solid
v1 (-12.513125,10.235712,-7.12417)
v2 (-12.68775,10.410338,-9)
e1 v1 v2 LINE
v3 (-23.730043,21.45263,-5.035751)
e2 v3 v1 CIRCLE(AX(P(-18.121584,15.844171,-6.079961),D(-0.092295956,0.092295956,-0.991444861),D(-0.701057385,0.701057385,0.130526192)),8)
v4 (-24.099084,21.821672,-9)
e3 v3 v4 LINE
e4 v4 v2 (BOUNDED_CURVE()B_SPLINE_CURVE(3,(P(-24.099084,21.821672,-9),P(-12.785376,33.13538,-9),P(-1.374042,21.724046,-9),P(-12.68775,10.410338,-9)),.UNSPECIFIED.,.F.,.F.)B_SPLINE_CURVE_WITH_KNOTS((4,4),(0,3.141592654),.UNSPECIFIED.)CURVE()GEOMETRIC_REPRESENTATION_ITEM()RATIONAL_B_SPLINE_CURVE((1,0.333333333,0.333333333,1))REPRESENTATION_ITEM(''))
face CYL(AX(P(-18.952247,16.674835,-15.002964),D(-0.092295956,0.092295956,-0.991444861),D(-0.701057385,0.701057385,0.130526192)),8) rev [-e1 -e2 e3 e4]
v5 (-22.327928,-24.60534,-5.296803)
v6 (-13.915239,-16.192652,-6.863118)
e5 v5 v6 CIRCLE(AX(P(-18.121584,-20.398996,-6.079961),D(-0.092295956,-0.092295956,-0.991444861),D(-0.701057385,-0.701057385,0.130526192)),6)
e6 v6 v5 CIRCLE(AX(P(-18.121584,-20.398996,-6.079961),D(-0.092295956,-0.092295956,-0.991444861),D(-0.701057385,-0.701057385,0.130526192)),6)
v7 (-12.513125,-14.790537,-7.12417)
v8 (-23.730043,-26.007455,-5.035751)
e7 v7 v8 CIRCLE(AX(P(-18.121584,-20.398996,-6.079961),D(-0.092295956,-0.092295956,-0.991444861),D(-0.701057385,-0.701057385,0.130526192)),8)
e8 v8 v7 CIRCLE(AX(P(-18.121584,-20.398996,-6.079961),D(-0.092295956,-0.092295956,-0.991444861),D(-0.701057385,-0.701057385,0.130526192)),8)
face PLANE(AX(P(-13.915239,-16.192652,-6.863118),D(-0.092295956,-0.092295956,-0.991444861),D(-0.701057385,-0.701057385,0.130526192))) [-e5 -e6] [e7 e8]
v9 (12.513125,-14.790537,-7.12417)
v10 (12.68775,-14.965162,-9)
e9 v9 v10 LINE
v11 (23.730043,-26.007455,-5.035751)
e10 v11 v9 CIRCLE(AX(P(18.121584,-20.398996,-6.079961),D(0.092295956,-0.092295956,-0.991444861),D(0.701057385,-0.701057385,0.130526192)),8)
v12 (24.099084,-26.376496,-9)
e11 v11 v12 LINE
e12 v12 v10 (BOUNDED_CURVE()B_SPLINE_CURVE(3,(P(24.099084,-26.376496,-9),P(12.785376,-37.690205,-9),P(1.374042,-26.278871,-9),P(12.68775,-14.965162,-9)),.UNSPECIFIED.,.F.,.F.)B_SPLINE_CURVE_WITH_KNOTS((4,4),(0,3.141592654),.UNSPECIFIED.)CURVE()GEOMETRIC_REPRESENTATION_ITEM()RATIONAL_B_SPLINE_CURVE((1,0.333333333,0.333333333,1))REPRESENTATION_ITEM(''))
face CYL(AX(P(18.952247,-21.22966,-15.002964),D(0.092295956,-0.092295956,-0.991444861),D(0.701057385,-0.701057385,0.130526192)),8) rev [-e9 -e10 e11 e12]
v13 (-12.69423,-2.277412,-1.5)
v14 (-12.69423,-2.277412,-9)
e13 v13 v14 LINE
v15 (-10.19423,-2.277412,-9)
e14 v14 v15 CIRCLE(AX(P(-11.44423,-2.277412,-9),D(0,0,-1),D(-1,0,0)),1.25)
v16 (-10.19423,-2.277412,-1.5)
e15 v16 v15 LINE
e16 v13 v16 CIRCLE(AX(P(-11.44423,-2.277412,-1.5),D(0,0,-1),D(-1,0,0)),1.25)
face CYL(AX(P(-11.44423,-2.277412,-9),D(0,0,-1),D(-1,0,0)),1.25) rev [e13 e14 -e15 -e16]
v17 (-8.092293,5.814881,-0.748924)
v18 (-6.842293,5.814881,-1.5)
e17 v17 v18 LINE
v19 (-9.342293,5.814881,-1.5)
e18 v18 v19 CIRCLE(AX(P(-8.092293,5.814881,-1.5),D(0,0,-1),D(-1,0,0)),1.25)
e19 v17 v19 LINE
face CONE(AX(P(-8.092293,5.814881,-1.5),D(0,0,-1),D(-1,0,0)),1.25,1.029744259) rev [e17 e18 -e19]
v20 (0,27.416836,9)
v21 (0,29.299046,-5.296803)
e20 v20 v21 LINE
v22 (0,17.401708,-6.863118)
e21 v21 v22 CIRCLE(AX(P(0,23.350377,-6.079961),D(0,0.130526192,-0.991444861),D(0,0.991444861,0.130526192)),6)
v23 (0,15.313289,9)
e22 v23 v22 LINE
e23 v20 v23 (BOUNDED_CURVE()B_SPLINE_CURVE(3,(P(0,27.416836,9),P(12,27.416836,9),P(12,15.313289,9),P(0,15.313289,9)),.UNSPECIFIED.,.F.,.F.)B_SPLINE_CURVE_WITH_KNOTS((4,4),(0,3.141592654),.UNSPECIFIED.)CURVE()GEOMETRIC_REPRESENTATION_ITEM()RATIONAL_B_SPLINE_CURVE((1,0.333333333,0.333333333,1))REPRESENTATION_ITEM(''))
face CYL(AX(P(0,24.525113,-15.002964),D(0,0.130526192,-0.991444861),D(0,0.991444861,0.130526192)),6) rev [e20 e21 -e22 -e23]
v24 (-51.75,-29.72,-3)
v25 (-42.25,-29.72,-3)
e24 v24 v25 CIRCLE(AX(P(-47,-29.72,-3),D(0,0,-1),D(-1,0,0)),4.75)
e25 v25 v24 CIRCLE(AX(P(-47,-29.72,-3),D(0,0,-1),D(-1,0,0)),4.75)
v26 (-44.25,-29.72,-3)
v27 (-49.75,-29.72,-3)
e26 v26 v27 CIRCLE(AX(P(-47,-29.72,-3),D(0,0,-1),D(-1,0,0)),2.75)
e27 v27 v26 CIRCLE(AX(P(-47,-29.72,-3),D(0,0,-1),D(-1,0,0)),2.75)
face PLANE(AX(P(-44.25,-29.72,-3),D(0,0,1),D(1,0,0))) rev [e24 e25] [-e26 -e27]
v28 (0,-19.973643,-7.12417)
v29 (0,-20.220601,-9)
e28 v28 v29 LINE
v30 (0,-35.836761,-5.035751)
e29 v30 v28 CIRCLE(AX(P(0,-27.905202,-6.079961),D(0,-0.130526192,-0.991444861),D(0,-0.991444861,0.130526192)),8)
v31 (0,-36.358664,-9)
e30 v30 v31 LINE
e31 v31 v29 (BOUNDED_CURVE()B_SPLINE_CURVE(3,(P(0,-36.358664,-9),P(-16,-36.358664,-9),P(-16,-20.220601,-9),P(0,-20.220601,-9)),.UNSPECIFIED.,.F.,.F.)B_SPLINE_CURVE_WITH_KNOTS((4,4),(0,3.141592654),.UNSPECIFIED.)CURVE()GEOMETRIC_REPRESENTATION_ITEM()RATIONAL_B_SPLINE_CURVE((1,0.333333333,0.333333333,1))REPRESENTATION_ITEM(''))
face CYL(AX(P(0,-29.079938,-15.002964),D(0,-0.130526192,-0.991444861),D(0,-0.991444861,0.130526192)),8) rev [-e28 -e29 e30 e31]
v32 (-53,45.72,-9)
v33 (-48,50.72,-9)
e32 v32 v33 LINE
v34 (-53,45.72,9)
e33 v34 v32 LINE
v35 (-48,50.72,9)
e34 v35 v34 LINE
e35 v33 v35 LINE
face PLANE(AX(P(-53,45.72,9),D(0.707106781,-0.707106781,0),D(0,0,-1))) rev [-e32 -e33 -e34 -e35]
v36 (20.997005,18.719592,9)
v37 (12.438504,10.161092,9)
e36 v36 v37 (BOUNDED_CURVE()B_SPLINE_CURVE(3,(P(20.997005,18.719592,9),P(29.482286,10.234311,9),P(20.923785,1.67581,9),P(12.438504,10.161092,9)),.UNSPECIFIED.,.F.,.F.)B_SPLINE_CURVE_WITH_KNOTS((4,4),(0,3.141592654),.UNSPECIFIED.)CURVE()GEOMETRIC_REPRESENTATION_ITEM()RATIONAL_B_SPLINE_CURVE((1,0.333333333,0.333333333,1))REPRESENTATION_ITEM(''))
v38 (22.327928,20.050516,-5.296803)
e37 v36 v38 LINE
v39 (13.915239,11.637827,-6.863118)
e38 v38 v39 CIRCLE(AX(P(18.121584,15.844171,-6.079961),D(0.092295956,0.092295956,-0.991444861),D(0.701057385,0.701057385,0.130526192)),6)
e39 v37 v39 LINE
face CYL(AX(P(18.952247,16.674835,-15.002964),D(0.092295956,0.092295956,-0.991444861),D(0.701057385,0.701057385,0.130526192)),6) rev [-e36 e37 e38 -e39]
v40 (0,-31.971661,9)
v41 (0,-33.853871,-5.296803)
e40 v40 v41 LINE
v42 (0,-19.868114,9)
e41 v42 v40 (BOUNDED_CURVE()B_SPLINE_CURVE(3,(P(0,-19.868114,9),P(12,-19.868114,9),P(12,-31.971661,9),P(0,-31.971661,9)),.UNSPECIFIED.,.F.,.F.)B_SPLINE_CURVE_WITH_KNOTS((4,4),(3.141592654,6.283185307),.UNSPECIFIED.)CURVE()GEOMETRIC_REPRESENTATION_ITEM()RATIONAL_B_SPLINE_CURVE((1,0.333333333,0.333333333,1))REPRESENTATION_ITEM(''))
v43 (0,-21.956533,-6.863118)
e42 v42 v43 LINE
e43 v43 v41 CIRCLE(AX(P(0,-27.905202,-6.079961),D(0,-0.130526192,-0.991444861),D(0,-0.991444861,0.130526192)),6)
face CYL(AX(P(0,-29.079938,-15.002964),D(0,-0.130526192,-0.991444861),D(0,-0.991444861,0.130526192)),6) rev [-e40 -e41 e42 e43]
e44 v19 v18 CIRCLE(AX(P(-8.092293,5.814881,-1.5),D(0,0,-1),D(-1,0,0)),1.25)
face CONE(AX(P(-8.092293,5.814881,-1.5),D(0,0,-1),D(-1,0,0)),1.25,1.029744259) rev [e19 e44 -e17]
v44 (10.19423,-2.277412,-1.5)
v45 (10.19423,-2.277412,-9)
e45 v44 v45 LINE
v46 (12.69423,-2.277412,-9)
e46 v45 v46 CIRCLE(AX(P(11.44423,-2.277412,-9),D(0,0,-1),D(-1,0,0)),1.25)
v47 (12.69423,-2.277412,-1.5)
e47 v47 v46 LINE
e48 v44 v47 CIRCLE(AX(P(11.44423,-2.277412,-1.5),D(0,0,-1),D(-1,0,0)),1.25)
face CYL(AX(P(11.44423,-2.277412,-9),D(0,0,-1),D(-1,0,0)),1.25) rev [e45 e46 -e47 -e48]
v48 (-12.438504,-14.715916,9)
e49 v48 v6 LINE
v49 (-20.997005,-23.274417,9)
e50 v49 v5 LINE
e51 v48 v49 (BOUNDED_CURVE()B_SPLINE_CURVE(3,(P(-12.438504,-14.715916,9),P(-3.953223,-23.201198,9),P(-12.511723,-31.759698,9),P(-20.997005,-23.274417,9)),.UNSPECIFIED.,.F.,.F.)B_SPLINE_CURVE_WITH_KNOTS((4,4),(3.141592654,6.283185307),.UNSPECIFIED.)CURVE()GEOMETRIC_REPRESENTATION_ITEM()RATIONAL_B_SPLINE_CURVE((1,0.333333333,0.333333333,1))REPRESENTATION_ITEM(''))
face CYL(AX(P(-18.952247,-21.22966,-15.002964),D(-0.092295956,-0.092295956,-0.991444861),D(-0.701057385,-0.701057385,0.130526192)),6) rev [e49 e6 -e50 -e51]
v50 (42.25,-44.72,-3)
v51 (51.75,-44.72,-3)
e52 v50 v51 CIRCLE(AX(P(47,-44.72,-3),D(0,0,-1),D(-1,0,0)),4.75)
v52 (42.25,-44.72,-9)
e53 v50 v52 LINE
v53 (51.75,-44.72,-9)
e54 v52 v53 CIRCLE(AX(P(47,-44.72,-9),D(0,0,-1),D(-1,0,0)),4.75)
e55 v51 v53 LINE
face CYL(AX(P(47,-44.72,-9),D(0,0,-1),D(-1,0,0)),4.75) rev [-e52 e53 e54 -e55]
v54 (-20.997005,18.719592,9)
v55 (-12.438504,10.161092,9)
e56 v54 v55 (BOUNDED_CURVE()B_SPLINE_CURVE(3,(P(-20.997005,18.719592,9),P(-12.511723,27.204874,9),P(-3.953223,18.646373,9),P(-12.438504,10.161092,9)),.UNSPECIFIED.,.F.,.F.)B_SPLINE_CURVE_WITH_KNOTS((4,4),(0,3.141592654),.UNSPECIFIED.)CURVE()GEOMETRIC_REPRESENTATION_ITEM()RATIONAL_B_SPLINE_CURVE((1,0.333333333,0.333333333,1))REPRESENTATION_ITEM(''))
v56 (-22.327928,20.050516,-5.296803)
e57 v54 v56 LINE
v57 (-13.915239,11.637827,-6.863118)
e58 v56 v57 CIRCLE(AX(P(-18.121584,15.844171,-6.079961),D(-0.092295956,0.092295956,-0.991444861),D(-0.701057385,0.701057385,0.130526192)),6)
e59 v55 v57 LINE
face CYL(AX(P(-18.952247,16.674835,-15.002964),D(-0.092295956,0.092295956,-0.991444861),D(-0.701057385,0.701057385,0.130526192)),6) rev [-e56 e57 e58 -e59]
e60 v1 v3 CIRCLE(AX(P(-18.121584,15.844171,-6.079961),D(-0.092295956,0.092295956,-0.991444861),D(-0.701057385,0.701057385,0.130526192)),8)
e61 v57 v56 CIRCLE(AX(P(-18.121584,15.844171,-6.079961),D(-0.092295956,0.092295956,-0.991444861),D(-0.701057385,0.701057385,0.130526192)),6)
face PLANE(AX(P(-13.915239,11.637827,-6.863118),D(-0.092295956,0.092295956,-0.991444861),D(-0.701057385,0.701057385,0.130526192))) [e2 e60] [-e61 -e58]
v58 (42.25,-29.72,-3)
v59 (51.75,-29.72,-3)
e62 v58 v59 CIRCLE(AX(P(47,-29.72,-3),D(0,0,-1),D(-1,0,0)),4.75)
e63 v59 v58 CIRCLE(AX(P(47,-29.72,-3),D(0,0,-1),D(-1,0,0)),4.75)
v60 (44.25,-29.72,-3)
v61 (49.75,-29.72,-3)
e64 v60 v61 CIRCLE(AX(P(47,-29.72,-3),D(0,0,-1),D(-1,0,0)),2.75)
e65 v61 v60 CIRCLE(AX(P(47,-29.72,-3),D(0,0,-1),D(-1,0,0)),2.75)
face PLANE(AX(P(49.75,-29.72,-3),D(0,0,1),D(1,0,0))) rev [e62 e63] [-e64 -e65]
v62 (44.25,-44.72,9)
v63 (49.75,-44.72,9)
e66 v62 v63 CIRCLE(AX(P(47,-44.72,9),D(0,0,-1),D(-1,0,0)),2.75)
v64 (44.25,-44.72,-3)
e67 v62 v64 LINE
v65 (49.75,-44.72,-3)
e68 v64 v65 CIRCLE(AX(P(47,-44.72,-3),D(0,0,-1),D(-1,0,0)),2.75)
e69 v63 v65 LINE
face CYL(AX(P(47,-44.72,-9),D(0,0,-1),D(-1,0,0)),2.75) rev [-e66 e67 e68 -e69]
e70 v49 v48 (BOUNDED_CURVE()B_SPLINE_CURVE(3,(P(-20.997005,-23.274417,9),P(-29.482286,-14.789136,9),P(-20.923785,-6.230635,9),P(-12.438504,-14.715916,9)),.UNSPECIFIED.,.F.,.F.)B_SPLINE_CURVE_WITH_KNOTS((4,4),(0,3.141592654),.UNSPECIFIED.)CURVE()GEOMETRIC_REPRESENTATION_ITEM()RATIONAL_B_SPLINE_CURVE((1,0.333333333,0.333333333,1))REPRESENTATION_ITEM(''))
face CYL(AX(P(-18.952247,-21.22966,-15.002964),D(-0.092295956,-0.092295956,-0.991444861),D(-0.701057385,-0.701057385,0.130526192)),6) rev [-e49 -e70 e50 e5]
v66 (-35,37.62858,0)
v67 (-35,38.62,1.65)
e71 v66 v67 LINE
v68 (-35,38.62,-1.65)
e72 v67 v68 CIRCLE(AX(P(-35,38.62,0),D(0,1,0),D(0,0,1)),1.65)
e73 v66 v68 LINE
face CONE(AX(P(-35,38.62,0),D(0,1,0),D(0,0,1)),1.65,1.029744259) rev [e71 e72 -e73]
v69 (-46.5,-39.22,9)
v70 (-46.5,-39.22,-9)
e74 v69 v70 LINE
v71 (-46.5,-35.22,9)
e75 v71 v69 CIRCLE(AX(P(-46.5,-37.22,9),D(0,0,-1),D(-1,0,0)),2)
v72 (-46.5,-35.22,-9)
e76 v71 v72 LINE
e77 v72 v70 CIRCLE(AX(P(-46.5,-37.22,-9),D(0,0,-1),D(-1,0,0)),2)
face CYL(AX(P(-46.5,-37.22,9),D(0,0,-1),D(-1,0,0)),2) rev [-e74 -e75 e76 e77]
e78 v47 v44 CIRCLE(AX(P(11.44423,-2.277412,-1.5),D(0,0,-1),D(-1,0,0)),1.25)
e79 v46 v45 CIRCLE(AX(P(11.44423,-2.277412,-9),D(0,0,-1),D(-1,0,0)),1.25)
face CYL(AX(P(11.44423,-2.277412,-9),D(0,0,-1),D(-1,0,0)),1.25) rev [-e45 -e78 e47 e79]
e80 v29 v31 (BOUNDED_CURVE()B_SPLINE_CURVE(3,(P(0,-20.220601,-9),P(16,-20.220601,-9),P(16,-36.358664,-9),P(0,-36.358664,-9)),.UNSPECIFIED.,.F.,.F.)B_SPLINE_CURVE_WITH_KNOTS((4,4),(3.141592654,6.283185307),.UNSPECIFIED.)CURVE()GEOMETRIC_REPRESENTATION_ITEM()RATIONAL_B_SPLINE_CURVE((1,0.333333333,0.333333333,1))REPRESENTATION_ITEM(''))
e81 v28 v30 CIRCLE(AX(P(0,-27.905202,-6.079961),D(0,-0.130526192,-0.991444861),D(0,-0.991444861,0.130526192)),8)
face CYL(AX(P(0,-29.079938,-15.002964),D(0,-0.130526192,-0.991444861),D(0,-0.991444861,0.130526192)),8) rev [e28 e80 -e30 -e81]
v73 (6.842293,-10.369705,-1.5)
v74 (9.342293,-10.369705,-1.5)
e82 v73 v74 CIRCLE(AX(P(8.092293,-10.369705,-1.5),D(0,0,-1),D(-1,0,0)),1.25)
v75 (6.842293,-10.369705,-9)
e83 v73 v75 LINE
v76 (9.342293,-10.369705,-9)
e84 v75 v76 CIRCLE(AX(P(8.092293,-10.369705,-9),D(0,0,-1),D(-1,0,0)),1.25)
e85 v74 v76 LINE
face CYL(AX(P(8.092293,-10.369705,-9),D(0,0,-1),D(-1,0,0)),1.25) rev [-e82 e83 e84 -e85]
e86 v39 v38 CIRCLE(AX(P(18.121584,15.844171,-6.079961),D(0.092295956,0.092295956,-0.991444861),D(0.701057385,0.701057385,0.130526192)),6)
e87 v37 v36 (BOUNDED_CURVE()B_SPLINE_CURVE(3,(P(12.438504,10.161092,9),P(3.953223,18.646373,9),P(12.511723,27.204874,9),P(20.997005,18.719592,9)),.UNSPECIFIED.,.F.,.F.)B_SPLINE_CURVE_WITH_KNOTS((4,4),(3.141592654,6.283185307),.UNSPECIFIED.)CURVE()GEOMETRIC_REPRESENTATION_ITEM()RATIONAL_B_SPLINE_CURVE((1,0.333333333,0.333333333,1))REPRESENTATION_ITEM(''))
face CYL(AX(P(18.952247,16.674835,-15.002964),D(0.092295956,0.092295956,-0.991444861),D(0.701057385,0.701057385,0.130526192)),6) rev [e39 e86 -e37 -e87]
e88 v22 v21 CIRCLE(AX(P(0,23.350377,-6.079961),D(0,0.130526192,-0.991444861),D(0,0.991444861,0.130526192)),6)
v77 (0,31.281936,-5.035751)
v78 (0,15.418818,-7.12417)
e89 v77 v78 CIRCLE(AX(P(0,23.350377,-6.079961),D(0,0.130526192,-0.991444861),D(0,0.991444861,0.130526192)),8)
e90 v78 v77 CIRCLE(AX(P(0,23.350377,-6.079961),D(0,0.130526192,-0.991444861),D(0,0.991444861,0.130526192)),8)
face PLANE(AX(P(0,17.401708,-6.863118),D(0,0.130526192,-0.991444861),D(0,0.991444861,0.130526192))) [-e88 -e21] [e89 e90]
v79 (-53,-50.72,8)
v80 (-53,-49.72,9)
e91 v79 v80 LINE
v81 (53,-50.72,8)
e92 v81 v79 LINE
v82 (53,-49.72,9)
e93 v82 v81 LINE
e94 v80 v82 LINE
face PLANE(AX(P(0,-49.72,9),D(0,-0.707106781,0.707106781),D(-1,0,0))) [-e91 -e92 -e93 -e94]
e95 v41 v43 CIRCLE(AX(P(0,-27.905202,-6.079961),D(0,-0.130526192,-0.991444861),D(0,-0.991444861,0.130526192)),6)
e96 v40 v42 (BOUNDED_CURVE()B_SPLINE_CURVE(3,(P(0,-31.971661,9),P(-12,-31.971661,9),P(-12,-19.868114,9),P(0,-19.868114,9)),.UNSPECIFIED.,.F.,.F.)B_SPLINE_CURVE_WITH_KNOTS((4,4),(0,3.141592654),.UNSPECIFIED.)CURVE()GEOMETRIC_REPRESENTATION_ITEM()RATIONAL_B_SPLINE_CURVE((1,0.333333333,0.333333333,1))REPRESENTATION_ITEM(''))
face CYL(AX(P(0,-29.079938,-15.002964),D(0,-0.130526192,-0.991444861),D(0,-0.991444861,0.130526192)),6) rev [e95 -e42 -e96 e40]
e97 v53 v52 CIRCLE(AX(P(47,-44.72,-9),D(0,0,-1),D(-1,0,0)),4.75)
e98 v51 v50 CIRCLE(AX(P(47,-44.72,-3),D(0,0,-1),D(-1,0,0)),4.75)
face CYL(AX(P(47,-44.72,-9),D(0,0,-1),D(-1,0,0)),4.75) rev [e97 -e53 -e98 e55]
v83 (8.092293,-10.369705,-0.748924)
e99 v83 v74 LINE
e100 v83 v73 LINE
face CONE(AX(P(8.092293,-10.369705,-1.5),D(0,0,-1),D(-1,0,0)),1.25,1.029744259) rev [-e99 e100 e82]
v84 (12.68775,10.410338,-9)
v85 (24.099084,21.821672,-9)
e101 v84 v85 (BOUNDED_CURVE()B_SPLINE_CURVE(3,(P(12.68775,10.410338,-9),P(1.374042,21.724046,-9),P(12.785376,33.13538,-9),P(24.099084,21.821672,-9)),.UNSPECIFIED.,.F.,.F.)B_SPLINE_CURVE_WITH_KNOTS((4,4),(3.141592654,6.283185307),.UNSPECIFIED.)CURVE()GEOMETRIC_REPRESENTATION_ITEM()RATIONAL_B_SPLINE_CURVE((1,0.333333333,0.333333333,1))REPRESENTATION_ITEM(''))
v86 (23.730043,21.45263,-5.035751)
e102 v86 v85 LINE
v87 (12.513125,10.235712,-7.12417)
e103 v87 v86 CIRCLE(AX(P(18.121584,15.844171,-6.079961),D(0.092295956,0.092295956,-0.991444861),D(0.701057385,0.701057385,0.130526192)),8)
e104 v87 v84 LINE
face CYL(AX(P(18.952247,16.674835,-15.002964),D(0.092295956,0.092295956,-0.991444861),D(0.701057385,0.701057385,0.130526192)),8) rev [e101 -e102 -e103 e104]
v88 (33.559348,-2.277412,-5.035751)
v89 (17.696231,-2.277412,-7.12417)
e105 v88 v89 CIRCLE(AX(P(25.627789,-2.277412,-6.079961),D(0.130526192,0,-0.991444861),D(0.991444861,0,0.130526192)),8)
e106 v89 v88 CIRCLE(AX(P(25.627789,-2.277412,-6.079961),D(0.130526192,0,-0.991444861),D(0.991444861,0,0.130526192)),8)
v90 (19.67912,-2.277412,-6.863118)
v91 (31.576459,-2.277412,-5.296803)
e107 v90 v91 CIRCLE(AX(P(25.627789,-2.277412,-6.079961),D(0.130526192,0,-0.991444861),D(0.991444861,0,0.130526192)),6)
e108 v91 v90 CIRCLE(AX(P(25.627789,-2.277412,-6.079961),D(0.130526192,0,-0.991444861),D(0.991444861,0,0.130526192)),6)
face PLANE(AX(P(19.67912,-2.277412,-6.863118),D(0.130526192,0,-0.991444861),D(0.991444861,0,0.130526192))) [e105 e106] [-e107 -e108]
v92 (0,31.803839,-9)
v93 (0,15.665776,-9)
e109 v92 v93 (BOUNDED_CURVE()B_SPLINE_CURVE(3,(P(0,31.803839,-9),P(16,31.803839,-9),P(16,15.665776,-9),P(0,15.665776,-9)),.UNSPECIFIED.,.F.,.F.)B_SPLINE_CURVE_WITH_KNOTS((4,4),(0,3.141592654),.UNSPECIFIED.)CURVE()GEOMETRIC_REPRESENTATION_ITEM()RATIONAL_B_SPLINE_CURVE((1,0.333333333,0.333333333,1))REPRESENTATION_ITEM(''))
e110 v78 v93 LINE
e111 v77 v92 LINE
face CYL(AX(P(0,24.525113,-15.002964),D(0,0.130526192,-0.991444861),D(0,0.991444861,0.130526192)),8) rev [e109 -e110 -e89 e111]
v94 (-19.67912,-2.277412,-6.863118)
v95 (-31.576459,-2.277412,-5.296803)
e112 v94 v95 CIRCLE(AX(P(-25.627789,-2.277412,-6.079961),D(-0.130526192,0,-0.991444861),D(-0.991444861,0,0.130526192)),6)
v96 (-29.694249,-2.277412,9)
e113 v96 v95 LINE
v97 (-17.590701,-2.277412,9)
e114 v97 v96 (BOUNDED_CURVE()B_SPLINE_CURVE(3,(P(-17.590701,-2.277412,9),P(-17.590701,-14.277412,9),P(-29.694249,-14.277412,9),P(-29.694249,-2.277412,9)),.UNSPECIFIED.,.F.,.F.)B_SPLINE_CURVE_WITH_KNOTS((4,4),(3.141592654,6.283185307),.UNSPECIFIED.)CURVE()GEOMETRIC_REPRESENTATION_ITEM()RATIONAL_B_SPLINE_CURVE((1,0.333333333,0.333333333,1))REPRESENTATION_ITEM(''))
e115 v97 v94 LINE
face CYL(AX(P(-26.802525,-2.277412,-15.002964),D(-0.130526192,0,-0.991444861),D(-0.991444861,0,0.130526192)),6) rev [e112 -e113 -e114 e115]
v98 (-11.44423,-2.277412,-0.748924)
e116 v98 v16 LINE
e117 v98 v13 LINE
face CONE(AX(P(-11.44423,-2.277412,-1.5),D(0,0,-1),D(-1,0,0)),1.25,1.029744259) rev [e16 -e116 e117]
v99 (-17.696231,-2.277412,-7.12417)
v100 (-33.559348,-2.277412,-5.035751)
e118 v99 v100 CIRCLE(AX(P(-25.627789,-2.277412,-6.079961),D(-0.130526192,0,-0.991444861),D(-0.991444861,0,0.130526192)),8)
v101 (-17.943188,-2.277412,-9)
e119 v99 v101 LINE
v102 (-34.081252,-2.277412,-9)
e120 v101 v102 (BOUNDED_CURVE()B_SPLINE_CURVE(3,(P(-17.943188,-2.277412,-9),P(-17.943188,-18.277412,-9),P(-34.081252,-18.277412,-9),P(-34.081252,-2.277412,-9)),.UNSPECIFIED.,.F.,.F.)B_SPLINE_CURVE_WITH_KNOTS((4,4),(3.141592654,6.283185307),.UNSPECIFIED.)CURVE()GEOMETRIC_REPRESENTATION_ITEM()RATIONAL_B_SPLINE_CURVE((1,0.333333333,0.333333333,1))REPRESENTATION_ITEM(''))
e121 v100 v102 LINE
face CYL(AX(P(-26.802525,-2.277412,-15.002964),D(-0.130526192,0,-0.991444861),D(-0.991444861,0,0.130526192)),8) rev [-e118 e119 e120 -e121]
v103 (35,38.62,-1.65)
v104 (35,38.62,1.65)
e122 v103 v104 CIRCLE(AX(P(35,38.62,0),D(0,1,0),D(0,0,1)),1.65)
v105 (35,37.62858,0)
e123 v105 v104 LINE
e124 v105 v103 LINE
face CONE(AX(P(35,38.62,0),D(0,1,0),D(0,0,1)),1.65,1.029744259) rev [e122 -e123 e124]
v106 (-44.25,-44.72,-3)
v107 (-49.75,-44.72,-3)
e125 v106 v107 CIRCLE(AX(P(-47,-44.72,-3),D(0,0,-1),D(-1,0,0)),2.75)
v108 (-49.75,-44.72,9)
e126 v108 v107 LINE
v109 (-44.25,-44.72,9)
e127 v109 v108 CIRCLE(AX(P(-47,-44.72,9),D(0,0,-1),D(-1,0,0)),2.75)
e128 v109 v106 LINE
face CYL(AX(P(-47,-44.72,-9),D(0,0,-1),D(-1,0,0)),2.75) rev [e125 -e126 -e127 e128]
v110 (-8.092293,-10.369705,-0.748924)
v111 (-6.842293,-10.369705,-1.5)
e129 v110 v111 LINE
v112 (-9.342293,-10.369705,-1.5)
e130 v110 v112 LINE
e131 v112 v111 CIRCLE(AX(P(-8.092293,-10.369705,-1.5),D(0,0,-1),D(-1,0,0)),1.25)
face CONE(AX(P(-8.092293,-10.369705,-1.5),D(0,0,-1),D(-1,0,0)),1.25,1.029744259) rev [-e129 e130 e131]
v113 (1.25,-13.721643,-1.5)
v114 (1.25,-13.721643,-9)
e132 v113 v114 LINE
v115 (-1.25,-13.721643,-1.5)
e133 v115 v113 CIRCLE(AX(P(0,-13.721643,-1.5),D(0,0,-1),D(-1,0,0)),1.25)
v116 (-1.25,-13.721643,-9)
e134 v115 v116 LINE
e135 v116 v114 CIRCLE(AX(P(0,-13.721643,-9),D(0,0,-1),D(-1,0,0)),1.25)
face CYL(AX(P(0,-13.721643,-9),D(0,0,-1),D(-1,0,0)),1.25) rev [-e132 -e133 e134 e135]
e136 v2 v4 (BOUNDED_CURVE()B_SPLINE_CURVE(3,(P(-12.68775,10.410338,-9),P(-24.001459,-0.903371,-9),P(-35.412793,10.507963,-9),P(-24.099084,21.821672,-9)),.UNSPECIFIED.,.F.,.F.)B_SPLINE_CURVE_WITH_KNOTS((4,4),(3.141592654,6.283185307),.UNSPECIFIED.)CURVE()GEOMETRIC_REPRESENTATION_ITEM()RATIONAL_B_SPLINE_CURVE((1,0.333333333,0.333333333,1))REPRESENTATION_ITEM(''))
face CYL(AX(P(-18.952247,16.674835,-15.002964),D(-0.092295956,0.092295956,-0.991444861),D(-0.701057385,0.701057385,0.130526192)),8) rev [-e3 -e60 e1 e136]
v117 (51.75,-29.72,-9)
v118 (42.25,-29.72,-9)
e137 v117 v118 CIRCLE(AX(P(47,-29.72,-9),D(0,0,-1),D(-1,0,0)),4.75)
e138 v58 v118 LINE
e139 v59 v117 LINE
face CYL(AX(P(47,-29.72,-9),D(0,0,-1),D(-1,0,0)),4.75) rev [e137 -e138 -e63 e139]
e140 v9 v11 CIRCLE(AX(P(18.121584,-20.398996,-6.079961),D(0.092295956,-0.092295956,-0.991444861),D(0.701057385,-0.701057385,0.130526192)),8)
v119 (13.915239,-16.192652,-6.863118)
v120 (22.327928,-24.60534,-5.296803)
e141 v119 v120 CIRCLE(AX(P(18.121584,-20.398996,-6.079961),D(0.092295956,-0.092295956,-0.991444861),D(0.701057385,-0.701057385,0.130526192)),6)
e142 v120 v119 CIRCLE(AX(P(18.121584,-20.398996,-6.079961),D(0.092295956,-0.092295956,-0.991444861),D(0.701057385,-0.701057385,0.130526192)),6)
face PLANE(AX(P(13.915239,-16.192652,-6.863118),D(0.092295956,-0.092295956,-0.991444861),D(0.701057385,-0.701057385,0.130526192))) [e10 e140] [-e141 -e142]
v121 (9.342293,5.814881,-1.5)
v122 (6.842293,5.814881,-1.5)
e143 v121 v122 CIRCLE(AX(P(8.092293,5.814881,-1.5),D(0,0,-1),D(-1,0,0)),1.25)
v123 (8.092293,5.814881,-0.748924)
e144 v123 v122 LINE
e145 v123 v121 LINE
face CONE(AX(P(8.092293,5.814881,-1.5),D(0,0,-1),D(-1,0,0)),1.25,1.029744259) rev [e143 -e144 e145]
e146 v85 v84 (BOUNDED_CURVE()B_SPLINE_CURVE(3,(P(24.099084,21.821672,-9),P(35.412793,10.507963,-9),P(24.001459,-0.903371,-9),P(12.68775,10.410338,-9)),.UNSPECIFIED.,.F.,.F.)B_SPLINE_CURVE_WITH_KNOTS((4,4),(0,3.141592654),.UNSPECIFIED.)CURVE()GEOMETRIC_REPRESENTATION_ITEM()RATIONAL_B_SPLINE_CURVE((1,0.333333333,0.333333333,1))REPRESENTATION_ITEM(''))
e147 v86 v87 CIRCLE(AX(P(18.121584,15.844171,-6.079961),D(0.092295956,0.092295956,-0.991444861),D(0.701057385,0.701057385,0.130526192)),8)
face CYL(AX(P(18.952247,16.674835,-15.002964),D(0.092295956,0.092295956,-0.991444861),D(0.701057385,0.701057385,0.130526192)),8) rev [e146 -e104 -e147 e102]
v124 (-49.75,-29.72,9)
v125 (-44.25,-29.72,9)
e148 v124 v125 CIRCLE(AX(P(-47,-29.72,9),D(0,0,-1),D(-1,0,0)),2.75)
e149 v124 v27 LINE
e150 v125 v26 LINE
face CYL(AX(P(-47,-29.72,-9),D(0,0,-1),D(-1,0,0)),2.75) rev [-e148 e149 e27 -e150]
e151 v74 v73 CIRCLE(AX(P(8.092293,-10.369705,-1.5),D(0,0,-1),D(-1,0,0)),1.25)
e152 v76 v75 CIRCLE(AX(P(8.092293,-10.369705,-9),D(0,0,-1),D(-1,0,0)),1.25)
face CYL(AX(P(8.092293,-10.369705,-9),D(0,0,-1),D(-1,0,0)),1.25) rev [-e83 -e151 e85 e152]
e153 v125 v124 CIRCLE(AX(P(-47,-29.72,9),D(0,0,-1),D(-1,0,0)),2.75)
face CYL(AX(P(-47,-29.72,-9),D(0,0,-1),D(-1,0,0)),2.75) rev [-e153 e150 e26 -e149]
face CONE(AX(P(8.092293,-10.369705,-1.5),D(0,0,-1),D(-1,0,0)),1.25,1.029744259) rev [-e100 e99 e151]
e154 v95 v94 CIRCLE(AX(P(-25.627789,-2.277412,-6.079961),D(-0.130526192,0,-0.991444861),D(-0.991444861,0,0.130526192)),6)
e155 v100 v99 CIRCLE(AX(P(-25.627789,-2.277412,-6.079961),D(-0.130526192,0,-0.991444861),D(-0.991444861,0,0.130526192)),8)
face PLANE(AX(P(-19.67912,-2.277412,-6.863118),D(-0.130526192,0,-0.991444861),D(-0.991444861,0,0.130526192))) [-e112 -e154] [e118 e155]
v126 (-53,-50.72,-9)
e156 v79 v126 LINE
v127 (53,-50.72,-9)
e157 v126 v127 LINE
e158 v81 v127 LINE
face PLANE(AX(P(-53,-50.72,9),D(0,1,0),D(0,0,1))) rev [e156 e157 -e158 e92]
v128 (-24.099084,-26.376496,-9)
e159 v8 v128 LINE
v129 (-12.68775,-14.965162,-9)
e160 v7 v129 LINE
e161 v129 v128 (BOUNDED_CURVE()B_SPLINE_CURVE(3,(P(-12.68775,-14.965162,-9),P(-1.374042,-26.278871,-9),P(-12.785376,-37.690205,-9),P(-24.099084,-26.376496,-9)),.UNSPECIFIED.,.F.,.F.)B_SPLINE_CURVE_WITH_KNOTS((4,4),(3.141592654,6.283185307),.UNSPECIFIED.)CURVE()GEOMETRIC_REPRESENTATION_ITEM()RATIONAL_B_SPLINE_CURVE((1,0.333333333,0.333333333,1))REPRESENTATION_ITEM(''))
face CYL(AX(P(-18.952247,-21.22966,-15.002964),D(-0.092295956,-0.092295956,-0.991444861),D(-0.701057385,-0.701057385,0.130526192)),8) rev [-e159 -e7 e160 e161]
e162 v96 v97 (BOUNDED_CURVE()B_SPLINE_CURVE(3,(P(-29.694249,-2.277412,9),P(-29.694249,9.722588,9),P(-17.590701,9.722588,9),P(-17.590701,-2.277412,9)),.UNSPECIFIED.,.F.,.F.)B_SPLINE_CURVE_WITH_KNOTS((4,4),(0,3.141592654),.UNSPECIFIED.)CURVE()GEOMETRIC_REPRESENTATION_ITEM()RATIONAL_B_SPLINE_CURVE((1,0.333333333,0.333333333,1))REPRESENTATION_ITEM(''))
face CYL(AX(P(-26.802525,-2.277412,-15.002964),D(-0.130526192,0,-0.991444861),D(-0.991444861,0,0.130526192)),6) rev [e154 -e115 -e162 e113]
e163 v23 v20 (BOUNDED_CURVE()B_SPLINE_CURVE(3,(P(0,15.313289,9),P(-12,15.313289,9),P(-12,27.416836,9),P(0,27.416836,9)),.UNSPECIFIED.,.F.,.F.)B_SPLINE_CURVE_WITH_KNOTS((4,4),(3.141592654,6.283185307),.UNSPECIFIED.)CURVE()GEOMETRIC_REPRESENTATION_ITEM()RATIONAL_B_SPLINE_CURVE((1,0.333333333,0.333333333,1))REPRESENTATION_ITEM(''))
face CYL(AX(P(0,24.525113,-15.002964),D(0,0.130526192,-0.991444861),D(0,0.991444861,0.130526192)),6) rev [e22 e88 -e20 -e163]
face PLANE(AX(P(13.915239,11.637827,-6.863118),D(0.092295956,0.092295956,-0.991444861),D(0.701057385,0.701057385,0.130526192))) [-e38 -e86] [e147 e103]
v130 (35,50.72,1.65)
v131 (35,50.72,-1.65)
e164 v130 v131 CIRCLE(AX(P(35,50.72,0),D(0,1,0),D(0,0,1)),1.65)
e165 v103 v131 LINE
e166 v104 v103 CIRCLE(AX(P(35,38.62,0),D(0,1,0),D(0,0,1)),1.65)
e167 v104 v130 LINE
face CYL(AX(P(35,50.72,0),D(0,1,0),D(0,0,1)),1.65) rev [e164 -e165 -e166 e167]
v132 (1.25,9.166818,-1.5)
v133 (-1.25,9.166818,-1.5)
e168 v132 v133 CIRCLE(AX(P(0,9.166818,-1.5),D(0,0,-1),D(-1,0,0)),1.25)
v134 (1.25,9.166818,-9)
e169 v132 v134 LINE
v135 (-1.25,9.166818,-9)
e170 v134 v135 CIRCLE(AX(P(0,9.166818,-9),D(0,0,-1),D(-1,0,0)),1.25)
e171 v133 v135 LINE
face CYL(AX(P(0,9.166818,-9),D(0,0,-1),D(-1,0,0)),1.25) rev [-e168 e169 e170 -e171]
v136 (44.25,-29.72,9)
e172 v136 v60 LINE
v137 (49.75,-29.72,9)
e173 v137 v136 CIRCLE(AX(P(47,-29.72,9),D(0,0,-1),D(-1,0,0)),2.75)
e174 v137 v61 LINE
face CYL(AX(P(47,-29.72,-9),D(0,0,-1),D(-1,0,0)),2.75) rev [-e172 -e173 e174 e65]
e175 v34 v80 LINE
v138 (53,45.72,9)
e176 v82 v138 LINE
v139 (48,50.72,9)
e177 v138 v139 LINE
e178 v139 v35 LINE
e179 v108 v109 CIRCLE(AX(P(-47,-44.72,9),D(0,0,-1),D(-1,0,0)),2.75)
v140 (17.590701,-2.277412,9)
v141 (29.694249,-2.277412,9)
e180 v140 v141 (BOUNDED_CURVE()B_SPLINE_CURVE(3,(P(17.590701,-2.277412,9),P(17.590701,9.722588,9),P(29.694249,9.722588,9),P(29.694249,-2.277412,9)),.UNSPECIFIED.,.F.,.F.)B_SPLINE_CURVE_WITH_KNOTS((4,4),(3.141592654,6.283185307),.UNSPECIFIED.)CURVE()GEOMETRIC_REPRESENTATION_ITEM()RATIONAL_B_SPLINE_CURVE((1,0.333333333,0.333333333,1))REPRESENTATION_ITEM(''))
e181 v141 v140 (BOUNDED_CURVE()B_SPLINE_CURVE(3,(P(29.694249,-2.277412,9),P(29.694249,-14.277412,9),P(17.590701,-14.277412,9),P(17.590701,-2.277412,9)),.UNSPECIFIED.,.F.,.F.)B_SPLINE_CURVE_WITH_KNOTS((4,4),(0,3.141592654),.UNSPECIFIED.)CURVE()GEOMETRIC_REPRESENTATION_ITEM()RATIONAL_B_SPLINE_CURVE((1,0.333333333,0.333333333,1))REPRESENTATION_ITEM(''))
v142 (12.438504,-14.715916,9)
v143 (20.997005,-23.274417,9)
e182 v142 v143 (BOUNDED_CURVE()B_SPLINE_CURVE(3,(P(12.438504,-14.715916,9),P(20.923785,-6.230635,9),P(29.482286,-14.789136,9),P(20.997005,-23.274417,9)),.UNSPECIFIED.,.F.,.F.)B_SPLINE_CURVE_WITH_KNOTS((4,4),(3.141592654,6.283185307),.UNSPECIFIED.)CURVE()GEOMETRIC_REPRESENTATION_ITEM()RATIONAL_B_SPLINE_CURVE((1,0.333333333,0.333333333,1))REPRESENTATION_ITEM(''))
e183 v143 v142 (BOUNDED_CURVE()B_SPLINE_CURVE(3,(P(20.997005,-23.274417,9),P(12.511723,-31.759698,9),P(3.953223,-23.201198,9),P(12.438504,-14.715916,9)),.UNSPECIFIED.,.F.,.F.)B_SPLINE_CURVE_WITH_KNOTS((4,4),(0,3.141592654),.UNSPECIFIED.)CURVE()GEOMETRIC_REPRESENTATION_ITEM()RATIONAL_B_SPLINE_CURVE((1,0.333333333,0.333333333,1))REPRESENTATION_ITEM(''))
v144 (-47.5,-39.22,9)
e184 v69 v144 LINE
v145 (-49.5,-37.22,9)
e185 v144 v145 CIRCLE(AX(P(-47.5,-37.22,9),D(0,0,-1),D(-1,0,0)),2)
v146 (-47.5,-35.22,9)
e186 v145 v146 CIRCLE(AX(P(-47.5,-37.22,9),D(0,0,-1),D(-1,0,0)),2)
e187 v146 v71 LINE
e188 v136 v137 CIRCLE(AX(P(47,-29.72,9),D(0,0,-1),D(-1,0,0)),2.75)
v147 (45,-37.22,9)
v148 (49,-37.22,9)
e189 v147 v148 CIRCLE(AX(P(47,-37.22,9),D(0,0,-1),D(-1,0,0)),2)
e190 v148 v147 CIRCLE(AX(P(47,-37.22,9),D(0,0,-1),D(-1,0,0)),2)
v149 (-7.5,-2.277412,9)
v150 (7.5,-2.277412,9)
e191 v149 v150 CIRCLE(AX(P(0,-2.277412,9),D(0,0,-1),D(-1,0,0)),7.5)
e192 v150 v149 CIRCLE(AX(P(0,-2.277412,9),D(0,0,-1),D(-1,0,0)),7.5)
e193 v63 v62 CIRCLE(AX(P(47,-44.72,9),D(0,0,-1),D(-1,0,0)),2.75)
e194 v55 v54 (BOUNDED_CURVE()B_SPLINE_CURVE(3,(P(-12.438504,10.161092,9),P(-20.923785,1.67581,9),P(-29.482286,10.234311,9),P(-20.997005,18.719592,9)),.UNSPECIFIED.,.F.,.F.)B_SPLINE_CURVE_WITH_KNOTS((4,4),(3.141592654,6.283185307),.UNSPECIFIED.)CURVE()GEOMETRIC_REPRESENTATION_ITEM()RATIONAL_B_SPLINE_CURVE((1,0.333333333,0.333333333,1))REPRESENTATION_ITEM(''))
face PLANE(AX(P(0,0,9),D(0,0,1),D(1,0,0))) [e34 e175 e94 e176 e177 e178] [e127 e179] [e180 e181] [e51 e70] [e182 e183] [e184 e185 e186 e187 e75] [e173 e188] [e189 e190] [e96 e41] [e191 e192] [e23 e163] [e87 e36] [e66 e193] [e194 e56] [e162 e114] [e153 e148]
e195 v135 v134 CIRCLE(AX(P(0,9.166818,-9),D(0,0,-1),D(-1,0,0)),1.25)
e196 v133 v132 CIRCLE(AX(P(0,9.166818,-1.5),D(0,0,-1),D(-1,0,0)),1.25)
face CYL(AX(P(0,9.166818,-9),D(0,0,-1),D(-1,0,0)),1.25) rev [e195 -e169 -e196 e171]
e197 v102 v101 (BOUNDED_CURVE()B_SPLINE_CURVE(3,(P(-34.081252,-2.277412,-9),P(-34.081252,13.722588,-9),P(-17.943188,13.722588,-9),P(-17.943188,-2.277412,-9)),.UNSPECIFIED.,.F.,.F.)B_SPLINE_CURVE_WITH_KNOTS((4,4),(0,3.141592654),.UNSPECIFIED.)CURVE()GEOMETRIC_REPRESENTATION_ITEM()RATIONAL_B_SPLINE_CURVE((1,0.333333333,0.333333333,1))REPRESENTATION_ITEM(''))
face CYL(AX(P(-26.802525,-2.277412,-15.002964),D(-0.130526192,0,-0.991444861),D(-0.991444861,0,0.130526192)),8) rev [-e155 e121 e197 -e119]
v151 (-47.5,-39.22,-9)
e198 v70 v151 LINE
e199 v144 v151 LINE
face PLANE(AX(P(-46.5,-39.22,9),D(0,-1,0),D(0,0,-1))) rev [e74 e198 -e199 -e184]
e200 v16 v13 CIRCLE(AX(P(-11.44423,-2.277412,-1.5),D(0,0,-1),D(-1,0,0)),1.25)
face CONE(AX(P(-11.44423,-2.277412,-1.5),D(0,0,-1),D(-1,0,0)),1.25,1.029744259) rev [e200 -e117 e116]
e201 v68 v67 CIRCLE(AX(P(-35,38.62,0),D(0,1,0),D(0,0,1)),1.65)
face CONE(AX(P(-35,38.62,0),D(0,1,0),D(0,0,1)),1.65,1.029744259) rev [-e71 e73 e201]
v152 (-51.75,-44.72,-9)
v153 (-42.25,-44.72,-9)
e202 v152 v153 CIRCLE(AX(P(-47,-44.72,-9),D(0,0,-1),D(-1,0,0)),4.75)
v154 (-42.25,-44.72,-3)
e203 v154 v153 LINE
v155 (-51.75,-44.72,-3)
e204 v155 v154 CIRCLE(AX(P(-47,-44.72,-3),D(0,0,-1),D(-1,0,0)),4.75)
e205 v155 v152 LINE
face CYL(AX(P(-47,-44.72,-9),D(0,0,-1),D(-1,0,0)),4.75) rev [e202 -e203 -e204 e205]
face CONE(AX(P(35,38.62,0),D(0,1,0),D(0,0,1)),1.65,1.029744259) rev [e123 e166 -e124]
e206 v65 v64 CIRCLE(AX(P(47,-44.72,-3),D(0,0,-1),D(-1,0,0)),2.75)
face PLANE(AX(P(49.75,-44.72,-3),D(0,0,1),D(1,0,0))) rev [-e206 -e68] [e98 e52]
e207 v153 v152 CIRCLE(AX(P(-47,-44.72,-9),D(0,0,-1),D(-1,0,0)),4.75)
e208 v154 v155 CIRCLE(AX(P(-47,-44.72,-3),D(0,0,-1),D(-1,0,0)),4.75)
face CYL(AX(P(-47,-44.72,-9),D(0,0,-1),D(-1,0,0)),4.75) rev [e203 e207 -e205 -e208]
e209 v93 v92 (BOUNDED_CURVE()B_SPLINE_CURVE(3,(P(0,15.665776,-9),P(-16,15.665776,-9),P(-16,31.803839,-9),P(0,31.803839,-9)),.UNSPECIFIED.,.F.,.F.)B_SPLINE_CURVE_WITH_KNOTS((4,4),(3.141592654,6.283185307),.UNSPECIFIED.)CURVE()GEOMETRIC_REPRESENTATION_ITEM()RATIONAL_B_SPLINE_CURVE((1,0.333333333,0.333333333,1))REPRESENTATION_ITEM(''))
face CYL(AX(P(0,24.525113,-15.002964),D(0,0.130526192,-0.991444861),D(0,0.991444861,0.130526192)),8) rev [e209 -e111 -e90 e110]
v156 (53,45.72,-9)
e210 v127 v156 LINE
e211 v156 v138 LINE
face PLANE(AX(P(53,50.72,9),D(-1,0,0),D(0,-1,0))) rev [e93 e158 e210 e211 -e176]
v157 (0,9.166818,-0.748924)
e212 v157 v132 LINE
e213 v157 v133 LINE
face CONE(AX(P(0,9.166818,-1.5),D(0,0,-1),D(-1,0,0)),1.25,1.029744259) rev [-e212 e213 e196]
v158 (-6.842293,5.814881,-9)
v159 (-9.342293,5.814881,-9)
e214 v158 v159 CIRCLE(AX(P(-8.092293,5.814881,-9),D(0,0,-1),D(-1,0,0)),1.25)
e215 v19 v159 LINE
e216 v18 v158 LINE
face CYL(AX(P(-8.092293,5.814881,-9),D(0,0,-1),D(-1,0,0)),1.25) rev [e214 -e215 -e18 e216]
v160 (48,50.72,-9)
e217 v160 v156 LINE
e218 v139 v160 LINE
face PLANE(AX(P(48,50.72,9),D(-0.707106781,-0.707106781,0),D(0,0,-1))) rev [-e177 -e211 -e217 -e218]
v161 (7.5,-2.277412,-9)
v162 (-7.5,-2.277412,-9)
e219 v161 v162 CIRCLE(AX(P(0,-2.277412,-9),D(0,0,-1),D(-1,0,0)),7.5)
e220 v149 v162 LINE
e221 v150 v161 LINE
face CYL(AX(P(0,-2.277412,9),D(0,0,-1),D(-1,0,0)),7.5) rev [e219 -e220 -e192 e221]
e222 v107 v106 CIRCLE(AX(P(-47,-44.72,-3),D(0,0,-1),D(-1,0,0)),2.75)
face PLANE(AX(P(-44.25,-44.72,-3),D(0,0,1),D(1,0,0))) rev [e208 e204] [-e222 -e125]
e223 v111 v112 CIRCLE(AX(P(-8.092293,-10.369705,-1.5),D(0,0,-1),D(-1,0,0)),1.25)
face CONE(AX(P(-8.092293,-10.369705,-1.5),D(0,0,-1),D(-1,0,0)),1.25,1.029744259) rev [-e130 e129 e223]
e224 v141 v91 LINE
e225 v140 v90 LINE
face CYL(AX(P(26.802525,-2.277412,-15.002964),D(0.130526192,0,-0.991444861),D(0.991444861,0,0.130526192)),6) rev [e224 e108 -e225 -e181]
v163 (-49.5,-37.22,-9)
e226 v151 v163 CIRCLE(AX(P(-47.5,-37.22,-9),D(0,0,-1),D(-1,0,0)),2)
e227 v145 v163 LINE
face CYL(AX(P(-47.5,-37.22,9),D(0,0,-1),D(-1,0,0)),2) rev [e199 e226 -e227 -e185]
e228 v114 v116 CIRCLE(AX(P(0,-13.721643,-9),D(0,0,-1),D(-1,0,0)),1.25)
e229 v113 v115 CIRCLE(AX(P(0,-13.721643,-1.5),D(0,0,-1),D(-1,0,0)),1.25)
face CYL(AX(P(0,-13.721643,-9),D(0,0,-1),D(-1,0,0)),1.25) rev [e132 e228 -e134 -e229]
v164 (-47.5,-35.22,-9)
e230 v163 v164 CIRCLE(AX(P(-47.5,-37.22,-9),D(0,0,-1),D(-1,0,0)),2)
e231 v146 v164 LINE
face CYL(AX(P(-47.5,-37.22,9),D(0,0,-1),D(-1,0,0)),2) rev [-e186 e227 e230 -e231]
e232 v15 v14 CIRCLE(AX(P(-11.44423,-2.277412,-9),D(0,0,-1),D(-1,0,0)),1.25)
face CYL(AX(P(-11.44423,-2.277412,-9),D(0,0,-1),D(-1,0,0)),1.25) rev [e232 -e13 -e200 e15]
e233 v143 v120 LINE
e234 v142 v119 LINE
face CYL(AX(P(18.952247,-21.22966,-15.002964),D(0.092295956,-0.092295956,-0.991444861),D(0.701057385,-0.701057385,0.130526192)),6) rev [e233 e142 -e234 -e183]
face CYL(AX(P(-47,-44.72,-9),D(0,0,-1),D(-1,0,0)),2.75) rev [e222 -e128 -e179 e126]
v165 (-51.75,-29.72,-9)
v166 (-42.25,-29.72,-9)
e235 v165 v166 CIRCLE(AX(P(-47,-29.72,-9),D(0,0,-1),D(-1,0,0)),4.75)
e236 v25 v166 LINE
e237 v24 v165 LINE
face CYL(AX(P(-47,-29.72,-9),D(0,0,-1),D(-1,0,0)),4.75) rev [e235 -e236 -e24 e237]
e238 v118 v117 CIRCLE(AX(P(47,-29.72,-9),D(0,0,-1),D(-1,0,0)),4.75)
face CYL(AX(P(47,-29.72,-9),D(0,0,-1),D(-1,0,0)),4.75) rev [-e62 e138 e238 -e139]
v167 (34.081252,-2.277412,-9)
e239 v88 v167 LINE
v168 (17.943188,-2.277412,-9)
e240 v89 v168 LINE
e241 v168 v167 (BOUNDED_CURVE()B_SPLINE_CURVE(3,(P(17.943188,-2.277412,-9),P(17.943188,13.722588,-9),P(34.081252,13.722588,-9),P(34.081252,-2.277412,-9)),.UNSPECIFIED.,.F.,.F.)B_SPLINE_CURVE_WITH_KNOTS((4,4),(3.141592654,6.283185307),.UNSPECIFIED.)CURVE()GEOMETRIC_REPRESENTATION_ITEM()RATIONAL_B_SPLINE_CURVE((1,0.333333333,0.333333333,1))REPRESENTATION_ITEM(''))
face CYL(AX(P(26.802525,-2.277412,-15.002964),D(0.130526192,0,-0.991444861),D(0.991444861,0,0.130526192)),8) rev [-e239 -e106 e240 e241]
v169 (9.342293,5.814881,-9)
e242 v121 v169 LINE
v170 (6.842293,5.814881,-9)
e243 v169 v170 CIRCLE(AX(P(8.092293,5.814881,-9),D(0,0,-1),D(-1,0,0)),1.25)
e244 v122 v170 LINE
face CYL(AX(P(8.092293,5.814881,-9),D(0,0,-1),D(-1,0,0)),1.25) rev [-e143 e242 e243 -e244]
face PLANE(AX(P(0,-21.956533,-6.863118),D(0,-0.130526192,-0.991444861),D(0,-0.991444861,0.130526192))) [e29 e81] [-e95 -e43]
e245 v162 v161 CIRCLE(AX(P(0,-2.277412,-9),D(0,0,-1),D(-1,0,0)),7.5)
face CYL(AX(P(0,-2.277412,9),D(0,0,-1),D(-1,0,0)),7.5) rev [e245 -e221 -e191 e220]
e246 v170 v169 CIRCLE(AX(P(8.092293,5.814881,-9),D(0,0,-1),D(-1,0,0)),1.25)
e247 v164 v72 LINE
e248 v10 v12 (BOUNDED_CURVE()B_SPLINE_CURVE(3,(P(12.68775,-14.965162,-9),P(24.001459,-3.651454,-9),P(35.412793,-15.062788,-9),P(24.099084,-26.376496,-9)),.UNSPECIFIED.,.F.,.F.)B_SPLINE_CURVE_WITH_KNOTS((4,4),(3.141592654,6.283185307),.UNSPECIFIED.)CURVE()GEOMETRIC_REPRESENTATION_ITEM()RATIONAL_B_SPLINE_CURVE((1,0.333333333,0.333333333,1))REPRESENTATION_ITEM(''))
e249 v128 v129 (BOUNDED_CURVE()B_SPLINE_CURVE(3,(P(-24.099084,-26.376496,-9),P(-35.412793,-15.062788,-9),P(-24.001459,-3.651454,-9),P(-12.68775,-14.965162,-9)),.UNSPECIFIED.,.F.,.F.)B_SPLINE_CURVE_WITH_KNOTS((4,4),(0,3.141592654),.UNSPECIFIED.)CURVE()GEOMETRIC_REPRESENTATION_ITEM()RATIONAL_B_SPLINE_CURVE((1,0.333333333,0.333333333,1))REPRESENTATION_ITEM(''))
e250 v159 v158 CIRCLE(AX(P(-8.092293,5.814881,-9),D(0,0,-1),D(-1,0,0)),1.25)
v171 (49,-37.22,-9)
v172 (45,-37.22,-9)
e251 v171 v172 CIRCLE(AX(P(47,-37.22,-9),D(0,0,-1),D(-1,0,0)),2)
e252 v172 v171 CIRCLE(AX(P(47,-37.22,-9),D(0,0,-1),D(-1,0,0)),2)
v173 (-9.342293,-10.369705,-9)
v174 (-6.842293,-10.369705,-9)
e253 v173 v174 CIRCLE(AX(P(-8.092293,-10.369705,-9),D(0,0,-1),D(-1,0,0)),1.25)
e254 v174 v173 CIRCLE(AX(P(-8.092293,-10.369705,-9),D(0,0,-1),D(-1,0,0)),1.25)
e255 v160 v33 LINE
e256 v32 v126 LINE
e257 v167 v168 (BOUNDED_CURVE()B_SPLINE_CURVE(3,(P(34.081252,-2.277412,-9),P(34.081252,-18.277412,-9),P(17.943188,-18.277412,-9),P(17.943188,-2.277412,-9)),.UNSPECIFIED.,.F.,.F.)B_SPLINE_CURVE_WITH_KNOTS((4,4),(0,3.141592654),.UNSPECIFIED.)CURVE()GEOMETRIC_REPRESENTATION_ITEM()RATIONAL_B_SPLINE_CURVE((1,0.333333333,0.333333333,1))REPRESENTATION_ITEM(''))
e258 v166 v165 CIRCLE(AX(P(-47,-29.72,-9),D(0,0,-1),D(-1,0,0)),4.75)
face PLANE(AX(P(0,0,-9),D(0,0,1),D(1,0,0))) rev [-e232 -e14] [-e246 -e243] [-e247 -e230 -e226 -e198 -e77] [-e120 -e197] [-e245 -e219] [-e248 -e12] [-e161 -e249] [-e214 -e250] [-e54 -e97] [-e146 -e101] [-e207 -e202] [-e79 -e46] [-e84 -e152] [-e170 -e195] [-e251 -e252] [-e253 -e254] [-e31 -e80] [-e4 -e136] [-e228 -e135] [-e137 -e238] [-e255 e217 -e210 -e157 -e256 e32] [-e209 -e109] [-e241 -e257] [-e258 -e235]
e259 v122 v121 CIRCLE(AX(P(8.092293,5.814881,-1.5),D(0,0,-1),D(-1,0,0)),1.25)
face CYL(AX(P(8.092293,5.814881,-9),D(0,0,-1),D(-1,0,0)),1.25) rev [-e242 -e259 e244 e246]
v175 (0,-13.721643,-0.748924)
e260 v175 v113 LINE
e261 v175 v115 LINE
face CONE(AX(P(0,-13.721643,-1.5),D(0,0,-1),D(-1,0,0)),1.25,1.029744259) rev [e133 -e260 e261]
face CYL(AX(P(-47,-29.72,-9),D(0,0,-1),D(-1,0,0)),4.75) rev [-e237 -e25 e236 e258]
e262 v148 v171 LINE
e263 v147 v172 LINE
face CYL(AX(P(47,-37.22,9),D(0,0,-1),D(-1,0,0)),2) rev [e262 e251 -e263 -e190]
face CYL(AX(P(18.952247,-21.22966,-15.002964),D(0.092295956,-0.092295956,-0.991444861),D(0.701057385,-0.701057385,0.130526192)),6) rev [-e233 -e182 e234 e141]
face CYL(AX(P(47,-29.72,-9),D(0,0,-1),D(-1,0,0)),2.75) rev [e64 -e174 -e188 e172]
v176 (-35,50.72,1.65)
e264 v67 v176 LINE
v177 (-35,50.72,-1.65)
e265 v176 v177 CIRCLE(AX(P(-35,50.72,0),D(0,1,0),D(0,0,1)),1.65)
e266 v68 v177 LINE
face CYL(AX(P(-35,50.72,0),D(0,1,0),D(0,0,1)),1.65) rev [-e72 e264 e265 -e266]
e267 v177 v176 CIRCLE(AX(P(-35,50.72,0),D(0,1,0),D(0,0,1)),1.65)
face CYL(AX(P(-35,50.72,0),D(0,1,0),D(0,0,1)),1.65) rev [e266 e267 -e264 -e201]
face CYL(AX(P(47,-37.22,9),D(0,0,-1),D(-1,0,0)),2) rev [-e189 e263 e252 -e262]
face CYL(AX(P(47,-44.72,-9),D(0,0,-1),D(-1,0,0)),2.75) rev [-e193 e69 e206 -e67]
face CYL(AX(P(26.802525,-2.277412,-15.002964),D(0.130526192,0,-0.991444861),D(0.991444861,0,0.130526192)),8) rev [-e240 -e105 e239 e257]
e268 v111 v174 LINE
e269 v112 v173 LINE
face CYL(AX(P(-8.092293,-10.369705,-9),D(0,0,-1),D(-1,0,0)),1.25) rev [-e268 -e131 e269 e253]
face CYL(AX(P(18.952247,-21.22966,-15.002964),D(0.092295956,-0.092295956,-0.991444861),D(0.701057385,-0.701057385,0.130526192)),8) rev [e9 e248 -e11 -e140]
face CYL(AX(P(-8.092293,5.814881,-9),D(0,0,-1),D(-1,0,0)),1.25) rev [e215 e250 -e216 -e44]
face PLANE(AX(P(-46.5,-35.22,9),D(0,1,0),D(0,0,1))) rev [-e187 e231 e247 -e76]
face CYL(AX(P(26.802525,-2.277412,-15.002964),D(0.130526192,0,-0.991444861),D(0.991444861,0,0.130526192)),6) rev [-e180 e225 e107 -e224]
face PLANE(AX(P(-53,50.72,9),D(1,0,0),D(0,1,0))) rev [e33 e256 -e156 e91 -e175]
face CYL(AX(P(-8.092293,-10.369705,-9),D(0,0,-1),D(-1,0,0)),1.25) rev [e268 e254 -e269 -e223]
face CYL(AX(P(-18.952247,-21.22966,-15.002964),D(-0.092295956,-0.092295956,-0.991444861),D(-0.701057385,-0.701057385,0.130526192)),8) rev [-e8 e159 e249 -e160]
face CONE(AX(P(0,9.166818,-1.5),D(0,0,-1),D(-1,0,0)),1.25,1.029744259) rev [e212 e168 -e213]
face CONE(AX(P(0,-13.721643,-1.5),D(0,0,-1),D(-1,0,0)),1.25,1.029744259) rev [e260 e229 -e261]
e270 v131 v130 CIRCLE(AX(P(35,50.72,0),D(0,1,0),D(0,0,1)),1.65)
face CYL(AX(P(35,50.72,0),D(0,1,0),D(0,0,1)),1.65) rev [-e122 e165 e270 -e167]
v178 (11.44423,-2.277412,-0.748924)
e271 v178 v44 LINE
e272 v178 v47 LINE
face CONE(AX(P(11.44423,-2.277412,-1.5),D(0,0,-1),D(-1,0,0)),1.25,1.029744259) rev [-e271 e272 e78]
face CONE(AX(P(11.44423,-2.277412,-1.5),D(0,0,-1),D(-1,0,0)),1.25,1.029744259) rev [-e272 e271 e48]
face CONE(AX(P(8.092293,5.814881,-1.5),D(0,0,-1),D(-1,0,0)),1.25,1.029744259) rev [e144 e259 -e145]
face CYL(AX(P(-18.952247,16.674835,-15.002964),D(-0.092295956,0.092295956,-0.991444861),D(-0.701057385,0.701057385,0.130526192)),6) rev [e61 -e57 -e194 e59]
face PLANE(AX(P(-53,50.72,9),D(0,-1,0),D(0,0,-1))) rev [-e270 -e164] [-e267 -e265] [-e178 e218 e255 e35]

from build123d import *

# Parameters (mm, degrees)
SKETCH1_W                                            = 106
SKETCH1_H                                            = 101.44
BOSS_EXTRUDE1_DEPTH                                  = 9
SKETCH3_R                                            = 7.5
CUT_EXTRUDE1_DEPTH                                   = 76.534882008
CIRPATTERN1_COUNT                                    = 8
CHAMFER1_SIZE                                        = 5
CHAMFER2_SIZE                                        = 1
HOLE_SIZE_PER_SOCKET_HEAD_CAP_SCREW_TYPE_D           = 5.5
HOLE_SIZE_PER_SOCKET_HEAD_CAP_SCREW_TYPE_CBORE_D     = 9.5
HOLE_SIZE_PER_SOCKET_HEAD_CAP_SCREW_TYPE_CBORE_DEPTH = 6
M4_TAPPED_HOLE1_D                                    = 3.3
M4_TAPPED_HOLE1_DEPTH                                = 12.1
M4_TAPPED_HOLE1_TIP                                  = 0.991420021
SKETCH11_R                                           = 2
CUT_EXTRUDE2_DEPTH                                   = 76.534882008


with BuildPart() as part:
    # Sketch1 → Boss-Extrude1 (new, symmetric)
    with BuildSketch(Plane.XY):
        Rectangle(SKETCH1_W, SKETCH1_H)
    extrude(amount=BOSS_EXTRUDE1_DEPTH, both=True)

    # Sketch3 → Cut-Extrude1 (cut, through all)
    with BuildSketch(Plane(origin=(0, 0, -9), x_dir=(-1, 0, 0), z_dir=(0, 0, -1))):
        with Locations((0, -2.277412343)):
            Circle(SKETCH3_R)
    extrude(amount=-CUT_EXTRUDE1_DEPTH, mode=Mode.SUBTRACT)

    # Sketch2 → Cut-Revolve1 (revolve, cut)
    with BuildSketch(Plane(origin=(0, 0, 0), x_dir=(0, 0, -1), z_dir=(1, 0, 0)), mode=Mode.PRIVATE) as cut_revolve1_sk:
        Polygon((6.863117782, 17.401707924), (7.124170166, 15.418818201), (16.047173919, 16.593553931), (15.002964381, 24.525112822), (-9.783157153, 21.261958017), (-9, 15.313288849), align=None)
    cut_revolve1 = revolve(cut_revolve1_sk.sketch.rotate(Axis((0, 24.525112822, -15.002964381), (0, -0.1305261922200479, 0.9914448613738109)), 180), axis=Axis((0, 24.525112822, -15.002964381), (0, -0.1305261922200479, 0.9914448613738109)), mode=Mode.SUBTRACT)

    # Sketch4 → M3 Tapped Hole1 (revolve, cut)
    with BuildSketch(Plane(origin=(0, 9.166817967, -9), x_dir=(0, 1, 0), z_dir=(1, 0, 0))):
        Polygon((0, 0), (0, 8.251075774), (1.25, 7.5), (1.25, 0), align=None)
    m3_tapped_hole1 = revolve(axis=Axis((0, 9.166817967, -15.35), (0, 0, 1)), mode=Mode.SUBTRACT)

    # CirPattern1: Cut-Revolve1, M3 Tapped Hole1 ×8 about axis
    cirpattern1_axis = Axis((0, -2.277412343, 0), (0, 0, 1))
    add([cut_revolve1.rotate(cirpattern1_axis, i * 360 / CIRPATTERN1_COUNT) for i in range(1, CIRPATTERN1_COUNT)], mode=Mode.SUBTRACT)
    add([m3_tapped_hole1.rotate(cirpattern1_axis, i * 360 / CIRPATTERN1_COUNT) for i in range(1, CIRPATTERN1_COUNT)], mode=Mode.SUBTRACT)

    # Chamfer1
    chamfer1_edges = [part.edges().sort_by_distance(p)[0] for p in [
        (-53, 50.72, 0),
        (53, 50.72, 0),
    ]]
    chamfer(chamfer1_edges, length=CHAMFER1_SIZE)

    # Chamfer2
    chamfer2_edges = [part.edges().sort_by_distance(p)[0] for p in [
        (0, -50.72, 9),
    ]]
    chamfer(chamfer2_edges, length=CHAMFER2_SIZE)

    # Hole size per socket head cap screw type1 (through all)
    with Locations(Plane(origin=(0, 0, -9), x_dir=(-1, 0, 0), z_dir=(0, 0, -1))):
        with Locations((-47, -29.72), (-47, -44.72), (47, -44.72), (47, -29.72)):
            CounterBoreHole(HOLE_SIZE_PER_SOCKET_HEAD_CAP_SCREW_TYPE_D / 2, HOLE_SIZE_PER_SOCKET_HEAD_CAP_SCREW_TYPE_CBORE_D / 2, HOLE_SIZE_PER_SOCKET_HEAD_CAP_SCREW_TYPE_CBORE_DEPTH)

    # M4 Tapped Hole1
    with Locations(Plane(origin=(0, 50.72, 0), x_dir=(1, 0, 0), z_dir=(0, 1, 0))):
        with Locations((-35, 0), (35, 0)):
            Hole(M4_TAPPED_HOLE1_D / 2, depth=M4_TAPPED_HOLE1_DEPTH)
            with Locations((0, 0, -(M4_TAPPED_HOLE1_DEPTH + M4_TAPPED_HOLE1_TIP / 2))):  # 118° drill point
                Cone(0, M4_TAPPED_HOLE1_D / 2, M4_TAPPED_HOLE1_TIP, mode=Mode.SUBTRACT)

    # Sketch11 → Cut-Extrude2 (cut, through all)
    with BuildSketch(Plane(origin=(0, 0, -9), x_dir=(-1, 0, 0), z_dir=(0, 0, -1))):
        with Locations((-47, -37.22)):
            Circle(SKETCH11_R)
        with BuildLine():
            Line((46.5, -35.22), (47.5, -35.22))
            ThreePointArc((47.5, -35.22), (49.5, -37.22), (47.5, -39.22))
            Line((47.5, -39.22), (46.5, -39.22))
            ThreePointArc((46.5, -39.22), (44.5, -37.22), (46.5, -35.22))
        make_face()
    extrude(amount=-CUT_EXTRUDE2_DEPTH, mode=Mode.SUBTRACT)


solid = part.part
